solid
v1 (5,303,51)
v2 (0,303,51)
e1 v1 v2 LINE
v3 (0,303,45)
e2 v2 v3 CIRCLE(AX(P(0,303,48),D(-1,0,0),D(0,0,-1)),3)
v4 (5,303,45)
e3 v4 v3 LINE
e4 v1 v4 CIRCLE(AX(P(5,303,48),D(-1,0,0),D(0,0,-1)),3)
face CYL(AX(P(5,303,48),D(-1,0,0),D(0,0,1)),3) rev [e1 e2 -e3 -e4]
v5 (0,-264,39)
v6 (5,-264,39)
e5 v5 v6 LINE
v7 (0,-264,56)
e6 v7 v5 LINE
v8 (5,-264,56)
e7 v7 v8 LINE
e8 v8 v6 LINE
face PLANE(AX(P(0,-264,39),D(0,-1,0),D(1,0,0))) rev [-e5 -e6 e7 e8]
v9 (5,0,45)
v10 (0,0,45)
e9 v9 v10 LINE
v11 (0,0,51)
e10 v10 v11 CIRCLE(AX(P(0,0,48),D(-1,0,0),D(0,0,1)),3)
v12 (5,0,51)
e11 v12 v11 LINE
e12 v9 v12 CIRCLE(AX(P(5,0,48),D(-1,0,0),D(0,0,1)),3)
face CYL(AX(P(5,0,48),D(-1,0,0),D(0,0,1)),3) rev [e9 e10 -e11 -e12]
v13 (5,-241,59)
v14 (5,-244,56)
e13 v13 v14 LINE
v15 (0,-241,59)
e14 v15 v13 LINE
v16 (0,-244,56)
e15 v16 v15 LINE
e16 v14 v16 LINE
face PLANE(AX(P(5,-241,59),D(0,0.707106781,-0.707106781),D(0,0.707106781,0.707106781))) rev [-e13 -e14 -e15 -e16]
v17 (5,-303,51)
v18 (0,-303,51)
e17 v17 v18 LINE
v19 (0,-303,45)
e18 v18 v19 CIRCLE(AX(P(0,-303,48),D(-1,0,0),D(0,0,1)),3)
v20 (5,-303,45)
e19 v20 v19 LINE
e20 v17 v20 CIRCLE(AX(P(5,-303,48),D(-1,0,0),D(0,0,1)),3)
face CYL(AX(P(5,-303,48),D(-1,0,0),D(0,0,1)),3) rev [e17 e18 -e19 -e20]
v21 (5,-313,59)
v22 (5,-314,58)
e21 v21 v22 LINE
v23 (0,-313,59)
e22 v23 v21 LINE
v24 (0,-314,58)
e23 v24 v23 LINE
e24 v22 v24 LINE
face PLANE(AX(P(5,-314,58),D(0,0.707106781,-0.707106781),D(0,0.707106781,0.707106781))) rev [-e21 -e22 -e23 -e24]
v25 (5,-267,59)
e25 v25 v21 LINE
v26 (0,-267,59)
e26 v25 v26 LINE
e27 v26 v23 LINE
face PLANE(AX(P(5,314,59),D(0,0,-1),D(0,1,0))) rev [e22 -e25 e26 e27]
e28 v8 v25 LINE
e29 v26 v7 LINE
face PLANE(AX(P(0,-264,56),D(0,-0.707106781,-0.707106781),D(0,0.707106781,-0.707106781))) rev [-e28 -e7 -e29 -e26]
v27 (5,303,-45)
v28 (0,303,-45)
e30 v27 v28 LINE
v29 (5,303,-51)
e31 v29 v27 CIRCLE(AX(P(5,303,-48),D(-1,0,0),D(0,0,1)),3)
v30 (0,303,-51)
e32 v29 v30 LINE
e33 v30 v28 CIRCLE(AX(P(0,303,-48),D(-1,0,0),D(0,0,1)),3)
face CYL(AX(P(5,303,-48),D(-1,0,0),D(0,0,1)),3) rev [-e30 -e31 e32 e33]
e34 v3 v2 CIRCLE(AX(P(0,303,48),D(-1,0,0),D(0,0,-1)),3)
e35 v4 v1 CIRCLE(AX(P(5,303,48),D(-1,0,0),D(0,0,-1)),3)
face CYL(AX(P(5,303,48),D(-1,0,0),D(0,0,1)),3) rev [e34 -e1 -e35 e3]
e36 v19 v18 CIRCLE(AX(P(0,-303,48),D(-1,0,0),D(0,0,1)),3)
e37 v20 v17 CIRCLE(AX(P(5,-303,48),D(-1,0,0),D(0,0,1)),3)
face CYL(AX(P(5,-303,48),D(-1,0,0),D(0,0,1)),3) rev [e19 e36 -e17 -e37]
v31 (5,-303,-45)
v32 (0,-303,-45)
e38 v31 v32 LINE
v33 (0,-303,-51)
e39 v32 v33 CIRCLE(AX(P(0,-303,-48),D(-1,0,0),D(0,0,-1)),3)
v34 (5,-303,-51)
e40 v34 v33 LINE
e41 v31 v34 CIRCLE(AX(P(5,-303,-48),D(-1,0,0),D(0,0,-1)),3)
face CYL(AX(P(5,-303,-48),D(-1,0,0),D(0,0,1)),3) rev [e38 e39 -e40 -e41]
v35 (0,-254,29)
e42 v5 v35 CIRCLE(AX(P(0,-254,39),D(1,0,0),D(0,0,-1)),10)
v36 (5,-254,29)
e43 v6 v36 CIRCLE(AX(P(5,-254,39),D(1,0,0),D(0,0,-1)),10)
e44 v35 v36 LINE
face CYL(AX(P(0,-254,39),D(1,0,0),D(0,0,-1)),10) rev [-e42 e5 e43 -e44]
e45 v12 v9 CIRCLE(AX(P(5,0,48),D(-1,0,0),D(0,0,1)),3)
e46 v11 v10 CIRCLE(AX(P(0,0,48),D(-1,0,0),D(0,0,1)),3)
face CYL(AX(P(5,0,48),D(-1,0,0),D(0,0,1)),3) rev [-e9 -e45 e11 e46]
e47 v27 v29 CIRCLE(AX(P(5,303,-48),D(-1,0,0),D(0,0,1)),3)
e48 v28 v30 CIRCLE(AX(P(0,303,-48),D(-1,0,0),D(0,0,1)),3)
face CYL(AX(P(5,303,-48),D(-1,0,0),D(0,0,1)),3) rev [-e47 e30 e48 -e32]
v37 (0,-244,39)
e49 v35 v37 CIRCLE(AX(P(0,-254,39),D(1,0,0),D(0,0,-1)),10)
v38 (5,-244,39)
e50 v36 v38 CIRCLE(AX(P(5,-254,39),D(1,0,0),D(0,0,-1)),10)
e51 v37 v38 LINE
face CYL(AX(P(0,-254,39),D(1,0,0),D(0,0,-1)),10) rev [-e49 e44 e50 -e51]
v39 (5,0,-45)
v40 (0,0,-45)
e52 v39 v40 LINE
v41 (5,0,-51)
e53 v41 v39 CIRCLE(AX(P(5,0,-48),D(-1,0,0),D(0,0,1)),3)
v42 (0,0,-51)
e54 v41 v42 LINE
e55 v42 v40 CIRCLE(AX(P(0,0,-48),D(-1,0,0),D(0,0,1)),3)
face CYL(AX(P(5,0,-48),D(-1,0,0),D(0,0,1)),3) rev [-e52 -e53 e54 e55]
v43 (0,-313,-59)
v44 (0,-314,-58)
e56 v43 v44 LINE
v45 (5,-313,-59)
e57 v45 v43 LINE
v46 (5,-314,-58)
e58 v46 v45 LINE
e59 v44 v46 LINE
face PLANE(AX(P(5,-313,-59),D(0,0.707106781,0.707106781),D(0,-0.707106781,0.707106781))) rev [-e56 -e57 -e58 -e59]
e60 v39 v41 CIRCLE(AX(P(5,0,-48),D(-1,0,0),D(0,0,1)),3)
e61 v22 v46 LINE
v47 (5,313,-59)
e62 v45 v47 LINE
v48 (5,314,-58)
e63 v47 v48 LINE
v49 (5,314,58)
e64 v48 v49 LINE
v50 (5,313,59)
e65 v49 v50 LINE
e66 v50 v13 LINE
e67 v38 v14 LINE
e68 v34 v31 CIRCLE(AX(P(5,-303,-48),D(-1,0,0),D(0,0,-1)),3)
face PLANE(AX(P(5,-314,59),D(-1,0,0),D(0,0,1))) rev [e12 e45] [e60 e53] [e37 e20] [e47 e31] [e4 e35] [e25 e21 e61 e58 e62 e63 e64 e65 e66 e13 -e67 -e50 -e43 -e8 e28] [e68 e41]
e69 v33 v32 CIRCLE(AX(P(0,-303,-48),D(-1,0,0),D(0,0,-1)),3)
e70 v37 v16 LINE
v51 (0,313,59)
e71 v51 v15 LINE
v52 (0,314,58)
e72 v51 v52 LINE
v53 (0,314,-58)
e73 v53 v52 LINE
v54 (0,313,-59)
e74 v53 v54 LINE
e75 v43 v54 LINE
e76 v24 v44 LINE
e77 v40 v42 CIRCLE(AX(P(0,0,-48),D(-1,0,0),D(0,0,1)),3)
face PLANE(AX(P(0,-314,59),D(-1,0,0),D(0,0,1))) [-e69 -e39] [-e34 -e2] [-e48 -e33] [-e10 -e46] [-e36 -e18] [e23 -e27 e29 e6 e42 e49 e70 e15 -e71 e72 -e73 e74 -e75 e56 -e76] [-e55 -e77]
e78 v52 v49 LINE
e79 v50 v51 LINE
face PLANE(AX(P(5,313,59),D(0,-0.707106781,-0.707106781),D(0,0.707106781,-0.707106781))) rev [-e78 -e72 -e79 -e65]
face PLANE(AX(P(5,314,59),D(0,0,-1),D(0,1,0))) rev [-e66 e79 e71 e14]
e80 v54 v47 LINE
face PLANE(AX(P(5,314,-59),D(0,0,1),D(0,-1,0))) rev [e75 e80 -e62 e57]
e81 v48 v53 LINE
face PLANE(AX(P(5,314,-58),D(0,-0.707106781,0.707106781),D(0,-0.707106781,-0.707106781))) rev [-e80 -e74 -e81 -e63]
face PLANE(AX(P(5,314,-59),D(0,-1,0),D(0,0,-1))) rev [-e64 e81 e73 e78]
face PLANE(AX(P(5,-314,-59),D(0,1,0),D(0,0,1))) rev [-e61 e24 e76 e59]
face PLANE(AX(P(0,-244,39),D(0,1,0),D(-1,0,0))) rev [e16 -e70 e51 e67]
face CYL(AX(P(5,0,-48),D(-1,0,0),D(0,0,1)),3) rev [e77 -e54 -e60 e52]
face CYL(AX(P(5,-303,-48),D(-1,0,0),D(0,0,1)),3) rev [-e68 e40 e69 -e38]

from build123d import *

# Parameters (mm, degrees)
SKETCH_1_W          = 118
SKETCH_1_H          = 628
EXTRUDE_1_DEPTH     = 5
CHAMFER_1_SIZE      = 1
SKETCH_2_R          = 3
CUT_EXTRUDE_1_DEPTH = 320.534035746
CUT_EXTRUDE_2_DEPTH = 320.534035746
CHAMFER_2_SIZE      = 3


with BuildPart() as part:
    # 草图1 → 凸台-拉伸1 (new body)
    with BuildSketch(Plane(origin=(0, 0, 0), x_dir=(0, 0, -1), z_dir=(1, 0, 0))):
        Rectangle(SKETCH_1_W, SKETCH_1_H)
    extrude(amount=EXTRUDE_1_DEPTH)

    # 倒角1
    chamfer_1_edges = [part.edges().sort_by_distance(p)[0] for p in [
        (2.5, 314, 59),
        (2.5, 314, -59),
        (2.5, -314, -59),
        (2.5, -314, 59),
    ]]
    chamfer(chamfer_1_edges, length=CHAMFER_1_SIZE)

    # 草图2 → 切除-拉伸1 (cut, through all)
    with BuildSketch(Plane.ZY):
        with Locations((-48, 303)):
            Circle(SKETCH_2_R)
        with Locations(Location((-48, -303, 0), (0, 0, 180))):
            Circle(SKETCH_2_R)
        with Locations((48, -303)):
            Circle(SKETCH_2_R)
        with Locations(Location((48, 303, 0), (0, 0, 180))):
            Circle(SKETCH_2_R)
        with Locations((48, 0)):
            Circle(SKETCH_2_R)
        with Locations((-48, 0)):
            Circle(SKETCH_2_R)
    extrude(amount=-CUT_EXTRUDE_1_DEPTH, mode=Mode.SUBTRACT)

    # 草图3 → 切除-拉伸2 (cut, through all)
    with BuildSketch(Plane(origin=(5, 0, 0), x_dir=(0, 0, -1), z_dir=(1, 0, 0))):
        with BuildLine():
            Line((-39, -264), (-59, -264))
            ThreePointArc((-59, -264), (-69, -254), (-59, -244))
            Line((-59, -244), (-39, -244))
            ThreePointArc((-39, -244), (-29, -254), (-39, -264))
        make_face()
    extrude(amount=-CUT_EXTRUDE_2_DEPTH, mode=Mode.SUBTRACT)

    # 倒角2
    chamfer_2_edges = [part.edges().sort_by_distance(p)[0] for p in [
        (2.5, -264, 59),
        (2.5, -244, 59),
    ]]
    chamfer(chamfer_2_edges, length=CHAMFER_2_SIZE)


solid = part.part
